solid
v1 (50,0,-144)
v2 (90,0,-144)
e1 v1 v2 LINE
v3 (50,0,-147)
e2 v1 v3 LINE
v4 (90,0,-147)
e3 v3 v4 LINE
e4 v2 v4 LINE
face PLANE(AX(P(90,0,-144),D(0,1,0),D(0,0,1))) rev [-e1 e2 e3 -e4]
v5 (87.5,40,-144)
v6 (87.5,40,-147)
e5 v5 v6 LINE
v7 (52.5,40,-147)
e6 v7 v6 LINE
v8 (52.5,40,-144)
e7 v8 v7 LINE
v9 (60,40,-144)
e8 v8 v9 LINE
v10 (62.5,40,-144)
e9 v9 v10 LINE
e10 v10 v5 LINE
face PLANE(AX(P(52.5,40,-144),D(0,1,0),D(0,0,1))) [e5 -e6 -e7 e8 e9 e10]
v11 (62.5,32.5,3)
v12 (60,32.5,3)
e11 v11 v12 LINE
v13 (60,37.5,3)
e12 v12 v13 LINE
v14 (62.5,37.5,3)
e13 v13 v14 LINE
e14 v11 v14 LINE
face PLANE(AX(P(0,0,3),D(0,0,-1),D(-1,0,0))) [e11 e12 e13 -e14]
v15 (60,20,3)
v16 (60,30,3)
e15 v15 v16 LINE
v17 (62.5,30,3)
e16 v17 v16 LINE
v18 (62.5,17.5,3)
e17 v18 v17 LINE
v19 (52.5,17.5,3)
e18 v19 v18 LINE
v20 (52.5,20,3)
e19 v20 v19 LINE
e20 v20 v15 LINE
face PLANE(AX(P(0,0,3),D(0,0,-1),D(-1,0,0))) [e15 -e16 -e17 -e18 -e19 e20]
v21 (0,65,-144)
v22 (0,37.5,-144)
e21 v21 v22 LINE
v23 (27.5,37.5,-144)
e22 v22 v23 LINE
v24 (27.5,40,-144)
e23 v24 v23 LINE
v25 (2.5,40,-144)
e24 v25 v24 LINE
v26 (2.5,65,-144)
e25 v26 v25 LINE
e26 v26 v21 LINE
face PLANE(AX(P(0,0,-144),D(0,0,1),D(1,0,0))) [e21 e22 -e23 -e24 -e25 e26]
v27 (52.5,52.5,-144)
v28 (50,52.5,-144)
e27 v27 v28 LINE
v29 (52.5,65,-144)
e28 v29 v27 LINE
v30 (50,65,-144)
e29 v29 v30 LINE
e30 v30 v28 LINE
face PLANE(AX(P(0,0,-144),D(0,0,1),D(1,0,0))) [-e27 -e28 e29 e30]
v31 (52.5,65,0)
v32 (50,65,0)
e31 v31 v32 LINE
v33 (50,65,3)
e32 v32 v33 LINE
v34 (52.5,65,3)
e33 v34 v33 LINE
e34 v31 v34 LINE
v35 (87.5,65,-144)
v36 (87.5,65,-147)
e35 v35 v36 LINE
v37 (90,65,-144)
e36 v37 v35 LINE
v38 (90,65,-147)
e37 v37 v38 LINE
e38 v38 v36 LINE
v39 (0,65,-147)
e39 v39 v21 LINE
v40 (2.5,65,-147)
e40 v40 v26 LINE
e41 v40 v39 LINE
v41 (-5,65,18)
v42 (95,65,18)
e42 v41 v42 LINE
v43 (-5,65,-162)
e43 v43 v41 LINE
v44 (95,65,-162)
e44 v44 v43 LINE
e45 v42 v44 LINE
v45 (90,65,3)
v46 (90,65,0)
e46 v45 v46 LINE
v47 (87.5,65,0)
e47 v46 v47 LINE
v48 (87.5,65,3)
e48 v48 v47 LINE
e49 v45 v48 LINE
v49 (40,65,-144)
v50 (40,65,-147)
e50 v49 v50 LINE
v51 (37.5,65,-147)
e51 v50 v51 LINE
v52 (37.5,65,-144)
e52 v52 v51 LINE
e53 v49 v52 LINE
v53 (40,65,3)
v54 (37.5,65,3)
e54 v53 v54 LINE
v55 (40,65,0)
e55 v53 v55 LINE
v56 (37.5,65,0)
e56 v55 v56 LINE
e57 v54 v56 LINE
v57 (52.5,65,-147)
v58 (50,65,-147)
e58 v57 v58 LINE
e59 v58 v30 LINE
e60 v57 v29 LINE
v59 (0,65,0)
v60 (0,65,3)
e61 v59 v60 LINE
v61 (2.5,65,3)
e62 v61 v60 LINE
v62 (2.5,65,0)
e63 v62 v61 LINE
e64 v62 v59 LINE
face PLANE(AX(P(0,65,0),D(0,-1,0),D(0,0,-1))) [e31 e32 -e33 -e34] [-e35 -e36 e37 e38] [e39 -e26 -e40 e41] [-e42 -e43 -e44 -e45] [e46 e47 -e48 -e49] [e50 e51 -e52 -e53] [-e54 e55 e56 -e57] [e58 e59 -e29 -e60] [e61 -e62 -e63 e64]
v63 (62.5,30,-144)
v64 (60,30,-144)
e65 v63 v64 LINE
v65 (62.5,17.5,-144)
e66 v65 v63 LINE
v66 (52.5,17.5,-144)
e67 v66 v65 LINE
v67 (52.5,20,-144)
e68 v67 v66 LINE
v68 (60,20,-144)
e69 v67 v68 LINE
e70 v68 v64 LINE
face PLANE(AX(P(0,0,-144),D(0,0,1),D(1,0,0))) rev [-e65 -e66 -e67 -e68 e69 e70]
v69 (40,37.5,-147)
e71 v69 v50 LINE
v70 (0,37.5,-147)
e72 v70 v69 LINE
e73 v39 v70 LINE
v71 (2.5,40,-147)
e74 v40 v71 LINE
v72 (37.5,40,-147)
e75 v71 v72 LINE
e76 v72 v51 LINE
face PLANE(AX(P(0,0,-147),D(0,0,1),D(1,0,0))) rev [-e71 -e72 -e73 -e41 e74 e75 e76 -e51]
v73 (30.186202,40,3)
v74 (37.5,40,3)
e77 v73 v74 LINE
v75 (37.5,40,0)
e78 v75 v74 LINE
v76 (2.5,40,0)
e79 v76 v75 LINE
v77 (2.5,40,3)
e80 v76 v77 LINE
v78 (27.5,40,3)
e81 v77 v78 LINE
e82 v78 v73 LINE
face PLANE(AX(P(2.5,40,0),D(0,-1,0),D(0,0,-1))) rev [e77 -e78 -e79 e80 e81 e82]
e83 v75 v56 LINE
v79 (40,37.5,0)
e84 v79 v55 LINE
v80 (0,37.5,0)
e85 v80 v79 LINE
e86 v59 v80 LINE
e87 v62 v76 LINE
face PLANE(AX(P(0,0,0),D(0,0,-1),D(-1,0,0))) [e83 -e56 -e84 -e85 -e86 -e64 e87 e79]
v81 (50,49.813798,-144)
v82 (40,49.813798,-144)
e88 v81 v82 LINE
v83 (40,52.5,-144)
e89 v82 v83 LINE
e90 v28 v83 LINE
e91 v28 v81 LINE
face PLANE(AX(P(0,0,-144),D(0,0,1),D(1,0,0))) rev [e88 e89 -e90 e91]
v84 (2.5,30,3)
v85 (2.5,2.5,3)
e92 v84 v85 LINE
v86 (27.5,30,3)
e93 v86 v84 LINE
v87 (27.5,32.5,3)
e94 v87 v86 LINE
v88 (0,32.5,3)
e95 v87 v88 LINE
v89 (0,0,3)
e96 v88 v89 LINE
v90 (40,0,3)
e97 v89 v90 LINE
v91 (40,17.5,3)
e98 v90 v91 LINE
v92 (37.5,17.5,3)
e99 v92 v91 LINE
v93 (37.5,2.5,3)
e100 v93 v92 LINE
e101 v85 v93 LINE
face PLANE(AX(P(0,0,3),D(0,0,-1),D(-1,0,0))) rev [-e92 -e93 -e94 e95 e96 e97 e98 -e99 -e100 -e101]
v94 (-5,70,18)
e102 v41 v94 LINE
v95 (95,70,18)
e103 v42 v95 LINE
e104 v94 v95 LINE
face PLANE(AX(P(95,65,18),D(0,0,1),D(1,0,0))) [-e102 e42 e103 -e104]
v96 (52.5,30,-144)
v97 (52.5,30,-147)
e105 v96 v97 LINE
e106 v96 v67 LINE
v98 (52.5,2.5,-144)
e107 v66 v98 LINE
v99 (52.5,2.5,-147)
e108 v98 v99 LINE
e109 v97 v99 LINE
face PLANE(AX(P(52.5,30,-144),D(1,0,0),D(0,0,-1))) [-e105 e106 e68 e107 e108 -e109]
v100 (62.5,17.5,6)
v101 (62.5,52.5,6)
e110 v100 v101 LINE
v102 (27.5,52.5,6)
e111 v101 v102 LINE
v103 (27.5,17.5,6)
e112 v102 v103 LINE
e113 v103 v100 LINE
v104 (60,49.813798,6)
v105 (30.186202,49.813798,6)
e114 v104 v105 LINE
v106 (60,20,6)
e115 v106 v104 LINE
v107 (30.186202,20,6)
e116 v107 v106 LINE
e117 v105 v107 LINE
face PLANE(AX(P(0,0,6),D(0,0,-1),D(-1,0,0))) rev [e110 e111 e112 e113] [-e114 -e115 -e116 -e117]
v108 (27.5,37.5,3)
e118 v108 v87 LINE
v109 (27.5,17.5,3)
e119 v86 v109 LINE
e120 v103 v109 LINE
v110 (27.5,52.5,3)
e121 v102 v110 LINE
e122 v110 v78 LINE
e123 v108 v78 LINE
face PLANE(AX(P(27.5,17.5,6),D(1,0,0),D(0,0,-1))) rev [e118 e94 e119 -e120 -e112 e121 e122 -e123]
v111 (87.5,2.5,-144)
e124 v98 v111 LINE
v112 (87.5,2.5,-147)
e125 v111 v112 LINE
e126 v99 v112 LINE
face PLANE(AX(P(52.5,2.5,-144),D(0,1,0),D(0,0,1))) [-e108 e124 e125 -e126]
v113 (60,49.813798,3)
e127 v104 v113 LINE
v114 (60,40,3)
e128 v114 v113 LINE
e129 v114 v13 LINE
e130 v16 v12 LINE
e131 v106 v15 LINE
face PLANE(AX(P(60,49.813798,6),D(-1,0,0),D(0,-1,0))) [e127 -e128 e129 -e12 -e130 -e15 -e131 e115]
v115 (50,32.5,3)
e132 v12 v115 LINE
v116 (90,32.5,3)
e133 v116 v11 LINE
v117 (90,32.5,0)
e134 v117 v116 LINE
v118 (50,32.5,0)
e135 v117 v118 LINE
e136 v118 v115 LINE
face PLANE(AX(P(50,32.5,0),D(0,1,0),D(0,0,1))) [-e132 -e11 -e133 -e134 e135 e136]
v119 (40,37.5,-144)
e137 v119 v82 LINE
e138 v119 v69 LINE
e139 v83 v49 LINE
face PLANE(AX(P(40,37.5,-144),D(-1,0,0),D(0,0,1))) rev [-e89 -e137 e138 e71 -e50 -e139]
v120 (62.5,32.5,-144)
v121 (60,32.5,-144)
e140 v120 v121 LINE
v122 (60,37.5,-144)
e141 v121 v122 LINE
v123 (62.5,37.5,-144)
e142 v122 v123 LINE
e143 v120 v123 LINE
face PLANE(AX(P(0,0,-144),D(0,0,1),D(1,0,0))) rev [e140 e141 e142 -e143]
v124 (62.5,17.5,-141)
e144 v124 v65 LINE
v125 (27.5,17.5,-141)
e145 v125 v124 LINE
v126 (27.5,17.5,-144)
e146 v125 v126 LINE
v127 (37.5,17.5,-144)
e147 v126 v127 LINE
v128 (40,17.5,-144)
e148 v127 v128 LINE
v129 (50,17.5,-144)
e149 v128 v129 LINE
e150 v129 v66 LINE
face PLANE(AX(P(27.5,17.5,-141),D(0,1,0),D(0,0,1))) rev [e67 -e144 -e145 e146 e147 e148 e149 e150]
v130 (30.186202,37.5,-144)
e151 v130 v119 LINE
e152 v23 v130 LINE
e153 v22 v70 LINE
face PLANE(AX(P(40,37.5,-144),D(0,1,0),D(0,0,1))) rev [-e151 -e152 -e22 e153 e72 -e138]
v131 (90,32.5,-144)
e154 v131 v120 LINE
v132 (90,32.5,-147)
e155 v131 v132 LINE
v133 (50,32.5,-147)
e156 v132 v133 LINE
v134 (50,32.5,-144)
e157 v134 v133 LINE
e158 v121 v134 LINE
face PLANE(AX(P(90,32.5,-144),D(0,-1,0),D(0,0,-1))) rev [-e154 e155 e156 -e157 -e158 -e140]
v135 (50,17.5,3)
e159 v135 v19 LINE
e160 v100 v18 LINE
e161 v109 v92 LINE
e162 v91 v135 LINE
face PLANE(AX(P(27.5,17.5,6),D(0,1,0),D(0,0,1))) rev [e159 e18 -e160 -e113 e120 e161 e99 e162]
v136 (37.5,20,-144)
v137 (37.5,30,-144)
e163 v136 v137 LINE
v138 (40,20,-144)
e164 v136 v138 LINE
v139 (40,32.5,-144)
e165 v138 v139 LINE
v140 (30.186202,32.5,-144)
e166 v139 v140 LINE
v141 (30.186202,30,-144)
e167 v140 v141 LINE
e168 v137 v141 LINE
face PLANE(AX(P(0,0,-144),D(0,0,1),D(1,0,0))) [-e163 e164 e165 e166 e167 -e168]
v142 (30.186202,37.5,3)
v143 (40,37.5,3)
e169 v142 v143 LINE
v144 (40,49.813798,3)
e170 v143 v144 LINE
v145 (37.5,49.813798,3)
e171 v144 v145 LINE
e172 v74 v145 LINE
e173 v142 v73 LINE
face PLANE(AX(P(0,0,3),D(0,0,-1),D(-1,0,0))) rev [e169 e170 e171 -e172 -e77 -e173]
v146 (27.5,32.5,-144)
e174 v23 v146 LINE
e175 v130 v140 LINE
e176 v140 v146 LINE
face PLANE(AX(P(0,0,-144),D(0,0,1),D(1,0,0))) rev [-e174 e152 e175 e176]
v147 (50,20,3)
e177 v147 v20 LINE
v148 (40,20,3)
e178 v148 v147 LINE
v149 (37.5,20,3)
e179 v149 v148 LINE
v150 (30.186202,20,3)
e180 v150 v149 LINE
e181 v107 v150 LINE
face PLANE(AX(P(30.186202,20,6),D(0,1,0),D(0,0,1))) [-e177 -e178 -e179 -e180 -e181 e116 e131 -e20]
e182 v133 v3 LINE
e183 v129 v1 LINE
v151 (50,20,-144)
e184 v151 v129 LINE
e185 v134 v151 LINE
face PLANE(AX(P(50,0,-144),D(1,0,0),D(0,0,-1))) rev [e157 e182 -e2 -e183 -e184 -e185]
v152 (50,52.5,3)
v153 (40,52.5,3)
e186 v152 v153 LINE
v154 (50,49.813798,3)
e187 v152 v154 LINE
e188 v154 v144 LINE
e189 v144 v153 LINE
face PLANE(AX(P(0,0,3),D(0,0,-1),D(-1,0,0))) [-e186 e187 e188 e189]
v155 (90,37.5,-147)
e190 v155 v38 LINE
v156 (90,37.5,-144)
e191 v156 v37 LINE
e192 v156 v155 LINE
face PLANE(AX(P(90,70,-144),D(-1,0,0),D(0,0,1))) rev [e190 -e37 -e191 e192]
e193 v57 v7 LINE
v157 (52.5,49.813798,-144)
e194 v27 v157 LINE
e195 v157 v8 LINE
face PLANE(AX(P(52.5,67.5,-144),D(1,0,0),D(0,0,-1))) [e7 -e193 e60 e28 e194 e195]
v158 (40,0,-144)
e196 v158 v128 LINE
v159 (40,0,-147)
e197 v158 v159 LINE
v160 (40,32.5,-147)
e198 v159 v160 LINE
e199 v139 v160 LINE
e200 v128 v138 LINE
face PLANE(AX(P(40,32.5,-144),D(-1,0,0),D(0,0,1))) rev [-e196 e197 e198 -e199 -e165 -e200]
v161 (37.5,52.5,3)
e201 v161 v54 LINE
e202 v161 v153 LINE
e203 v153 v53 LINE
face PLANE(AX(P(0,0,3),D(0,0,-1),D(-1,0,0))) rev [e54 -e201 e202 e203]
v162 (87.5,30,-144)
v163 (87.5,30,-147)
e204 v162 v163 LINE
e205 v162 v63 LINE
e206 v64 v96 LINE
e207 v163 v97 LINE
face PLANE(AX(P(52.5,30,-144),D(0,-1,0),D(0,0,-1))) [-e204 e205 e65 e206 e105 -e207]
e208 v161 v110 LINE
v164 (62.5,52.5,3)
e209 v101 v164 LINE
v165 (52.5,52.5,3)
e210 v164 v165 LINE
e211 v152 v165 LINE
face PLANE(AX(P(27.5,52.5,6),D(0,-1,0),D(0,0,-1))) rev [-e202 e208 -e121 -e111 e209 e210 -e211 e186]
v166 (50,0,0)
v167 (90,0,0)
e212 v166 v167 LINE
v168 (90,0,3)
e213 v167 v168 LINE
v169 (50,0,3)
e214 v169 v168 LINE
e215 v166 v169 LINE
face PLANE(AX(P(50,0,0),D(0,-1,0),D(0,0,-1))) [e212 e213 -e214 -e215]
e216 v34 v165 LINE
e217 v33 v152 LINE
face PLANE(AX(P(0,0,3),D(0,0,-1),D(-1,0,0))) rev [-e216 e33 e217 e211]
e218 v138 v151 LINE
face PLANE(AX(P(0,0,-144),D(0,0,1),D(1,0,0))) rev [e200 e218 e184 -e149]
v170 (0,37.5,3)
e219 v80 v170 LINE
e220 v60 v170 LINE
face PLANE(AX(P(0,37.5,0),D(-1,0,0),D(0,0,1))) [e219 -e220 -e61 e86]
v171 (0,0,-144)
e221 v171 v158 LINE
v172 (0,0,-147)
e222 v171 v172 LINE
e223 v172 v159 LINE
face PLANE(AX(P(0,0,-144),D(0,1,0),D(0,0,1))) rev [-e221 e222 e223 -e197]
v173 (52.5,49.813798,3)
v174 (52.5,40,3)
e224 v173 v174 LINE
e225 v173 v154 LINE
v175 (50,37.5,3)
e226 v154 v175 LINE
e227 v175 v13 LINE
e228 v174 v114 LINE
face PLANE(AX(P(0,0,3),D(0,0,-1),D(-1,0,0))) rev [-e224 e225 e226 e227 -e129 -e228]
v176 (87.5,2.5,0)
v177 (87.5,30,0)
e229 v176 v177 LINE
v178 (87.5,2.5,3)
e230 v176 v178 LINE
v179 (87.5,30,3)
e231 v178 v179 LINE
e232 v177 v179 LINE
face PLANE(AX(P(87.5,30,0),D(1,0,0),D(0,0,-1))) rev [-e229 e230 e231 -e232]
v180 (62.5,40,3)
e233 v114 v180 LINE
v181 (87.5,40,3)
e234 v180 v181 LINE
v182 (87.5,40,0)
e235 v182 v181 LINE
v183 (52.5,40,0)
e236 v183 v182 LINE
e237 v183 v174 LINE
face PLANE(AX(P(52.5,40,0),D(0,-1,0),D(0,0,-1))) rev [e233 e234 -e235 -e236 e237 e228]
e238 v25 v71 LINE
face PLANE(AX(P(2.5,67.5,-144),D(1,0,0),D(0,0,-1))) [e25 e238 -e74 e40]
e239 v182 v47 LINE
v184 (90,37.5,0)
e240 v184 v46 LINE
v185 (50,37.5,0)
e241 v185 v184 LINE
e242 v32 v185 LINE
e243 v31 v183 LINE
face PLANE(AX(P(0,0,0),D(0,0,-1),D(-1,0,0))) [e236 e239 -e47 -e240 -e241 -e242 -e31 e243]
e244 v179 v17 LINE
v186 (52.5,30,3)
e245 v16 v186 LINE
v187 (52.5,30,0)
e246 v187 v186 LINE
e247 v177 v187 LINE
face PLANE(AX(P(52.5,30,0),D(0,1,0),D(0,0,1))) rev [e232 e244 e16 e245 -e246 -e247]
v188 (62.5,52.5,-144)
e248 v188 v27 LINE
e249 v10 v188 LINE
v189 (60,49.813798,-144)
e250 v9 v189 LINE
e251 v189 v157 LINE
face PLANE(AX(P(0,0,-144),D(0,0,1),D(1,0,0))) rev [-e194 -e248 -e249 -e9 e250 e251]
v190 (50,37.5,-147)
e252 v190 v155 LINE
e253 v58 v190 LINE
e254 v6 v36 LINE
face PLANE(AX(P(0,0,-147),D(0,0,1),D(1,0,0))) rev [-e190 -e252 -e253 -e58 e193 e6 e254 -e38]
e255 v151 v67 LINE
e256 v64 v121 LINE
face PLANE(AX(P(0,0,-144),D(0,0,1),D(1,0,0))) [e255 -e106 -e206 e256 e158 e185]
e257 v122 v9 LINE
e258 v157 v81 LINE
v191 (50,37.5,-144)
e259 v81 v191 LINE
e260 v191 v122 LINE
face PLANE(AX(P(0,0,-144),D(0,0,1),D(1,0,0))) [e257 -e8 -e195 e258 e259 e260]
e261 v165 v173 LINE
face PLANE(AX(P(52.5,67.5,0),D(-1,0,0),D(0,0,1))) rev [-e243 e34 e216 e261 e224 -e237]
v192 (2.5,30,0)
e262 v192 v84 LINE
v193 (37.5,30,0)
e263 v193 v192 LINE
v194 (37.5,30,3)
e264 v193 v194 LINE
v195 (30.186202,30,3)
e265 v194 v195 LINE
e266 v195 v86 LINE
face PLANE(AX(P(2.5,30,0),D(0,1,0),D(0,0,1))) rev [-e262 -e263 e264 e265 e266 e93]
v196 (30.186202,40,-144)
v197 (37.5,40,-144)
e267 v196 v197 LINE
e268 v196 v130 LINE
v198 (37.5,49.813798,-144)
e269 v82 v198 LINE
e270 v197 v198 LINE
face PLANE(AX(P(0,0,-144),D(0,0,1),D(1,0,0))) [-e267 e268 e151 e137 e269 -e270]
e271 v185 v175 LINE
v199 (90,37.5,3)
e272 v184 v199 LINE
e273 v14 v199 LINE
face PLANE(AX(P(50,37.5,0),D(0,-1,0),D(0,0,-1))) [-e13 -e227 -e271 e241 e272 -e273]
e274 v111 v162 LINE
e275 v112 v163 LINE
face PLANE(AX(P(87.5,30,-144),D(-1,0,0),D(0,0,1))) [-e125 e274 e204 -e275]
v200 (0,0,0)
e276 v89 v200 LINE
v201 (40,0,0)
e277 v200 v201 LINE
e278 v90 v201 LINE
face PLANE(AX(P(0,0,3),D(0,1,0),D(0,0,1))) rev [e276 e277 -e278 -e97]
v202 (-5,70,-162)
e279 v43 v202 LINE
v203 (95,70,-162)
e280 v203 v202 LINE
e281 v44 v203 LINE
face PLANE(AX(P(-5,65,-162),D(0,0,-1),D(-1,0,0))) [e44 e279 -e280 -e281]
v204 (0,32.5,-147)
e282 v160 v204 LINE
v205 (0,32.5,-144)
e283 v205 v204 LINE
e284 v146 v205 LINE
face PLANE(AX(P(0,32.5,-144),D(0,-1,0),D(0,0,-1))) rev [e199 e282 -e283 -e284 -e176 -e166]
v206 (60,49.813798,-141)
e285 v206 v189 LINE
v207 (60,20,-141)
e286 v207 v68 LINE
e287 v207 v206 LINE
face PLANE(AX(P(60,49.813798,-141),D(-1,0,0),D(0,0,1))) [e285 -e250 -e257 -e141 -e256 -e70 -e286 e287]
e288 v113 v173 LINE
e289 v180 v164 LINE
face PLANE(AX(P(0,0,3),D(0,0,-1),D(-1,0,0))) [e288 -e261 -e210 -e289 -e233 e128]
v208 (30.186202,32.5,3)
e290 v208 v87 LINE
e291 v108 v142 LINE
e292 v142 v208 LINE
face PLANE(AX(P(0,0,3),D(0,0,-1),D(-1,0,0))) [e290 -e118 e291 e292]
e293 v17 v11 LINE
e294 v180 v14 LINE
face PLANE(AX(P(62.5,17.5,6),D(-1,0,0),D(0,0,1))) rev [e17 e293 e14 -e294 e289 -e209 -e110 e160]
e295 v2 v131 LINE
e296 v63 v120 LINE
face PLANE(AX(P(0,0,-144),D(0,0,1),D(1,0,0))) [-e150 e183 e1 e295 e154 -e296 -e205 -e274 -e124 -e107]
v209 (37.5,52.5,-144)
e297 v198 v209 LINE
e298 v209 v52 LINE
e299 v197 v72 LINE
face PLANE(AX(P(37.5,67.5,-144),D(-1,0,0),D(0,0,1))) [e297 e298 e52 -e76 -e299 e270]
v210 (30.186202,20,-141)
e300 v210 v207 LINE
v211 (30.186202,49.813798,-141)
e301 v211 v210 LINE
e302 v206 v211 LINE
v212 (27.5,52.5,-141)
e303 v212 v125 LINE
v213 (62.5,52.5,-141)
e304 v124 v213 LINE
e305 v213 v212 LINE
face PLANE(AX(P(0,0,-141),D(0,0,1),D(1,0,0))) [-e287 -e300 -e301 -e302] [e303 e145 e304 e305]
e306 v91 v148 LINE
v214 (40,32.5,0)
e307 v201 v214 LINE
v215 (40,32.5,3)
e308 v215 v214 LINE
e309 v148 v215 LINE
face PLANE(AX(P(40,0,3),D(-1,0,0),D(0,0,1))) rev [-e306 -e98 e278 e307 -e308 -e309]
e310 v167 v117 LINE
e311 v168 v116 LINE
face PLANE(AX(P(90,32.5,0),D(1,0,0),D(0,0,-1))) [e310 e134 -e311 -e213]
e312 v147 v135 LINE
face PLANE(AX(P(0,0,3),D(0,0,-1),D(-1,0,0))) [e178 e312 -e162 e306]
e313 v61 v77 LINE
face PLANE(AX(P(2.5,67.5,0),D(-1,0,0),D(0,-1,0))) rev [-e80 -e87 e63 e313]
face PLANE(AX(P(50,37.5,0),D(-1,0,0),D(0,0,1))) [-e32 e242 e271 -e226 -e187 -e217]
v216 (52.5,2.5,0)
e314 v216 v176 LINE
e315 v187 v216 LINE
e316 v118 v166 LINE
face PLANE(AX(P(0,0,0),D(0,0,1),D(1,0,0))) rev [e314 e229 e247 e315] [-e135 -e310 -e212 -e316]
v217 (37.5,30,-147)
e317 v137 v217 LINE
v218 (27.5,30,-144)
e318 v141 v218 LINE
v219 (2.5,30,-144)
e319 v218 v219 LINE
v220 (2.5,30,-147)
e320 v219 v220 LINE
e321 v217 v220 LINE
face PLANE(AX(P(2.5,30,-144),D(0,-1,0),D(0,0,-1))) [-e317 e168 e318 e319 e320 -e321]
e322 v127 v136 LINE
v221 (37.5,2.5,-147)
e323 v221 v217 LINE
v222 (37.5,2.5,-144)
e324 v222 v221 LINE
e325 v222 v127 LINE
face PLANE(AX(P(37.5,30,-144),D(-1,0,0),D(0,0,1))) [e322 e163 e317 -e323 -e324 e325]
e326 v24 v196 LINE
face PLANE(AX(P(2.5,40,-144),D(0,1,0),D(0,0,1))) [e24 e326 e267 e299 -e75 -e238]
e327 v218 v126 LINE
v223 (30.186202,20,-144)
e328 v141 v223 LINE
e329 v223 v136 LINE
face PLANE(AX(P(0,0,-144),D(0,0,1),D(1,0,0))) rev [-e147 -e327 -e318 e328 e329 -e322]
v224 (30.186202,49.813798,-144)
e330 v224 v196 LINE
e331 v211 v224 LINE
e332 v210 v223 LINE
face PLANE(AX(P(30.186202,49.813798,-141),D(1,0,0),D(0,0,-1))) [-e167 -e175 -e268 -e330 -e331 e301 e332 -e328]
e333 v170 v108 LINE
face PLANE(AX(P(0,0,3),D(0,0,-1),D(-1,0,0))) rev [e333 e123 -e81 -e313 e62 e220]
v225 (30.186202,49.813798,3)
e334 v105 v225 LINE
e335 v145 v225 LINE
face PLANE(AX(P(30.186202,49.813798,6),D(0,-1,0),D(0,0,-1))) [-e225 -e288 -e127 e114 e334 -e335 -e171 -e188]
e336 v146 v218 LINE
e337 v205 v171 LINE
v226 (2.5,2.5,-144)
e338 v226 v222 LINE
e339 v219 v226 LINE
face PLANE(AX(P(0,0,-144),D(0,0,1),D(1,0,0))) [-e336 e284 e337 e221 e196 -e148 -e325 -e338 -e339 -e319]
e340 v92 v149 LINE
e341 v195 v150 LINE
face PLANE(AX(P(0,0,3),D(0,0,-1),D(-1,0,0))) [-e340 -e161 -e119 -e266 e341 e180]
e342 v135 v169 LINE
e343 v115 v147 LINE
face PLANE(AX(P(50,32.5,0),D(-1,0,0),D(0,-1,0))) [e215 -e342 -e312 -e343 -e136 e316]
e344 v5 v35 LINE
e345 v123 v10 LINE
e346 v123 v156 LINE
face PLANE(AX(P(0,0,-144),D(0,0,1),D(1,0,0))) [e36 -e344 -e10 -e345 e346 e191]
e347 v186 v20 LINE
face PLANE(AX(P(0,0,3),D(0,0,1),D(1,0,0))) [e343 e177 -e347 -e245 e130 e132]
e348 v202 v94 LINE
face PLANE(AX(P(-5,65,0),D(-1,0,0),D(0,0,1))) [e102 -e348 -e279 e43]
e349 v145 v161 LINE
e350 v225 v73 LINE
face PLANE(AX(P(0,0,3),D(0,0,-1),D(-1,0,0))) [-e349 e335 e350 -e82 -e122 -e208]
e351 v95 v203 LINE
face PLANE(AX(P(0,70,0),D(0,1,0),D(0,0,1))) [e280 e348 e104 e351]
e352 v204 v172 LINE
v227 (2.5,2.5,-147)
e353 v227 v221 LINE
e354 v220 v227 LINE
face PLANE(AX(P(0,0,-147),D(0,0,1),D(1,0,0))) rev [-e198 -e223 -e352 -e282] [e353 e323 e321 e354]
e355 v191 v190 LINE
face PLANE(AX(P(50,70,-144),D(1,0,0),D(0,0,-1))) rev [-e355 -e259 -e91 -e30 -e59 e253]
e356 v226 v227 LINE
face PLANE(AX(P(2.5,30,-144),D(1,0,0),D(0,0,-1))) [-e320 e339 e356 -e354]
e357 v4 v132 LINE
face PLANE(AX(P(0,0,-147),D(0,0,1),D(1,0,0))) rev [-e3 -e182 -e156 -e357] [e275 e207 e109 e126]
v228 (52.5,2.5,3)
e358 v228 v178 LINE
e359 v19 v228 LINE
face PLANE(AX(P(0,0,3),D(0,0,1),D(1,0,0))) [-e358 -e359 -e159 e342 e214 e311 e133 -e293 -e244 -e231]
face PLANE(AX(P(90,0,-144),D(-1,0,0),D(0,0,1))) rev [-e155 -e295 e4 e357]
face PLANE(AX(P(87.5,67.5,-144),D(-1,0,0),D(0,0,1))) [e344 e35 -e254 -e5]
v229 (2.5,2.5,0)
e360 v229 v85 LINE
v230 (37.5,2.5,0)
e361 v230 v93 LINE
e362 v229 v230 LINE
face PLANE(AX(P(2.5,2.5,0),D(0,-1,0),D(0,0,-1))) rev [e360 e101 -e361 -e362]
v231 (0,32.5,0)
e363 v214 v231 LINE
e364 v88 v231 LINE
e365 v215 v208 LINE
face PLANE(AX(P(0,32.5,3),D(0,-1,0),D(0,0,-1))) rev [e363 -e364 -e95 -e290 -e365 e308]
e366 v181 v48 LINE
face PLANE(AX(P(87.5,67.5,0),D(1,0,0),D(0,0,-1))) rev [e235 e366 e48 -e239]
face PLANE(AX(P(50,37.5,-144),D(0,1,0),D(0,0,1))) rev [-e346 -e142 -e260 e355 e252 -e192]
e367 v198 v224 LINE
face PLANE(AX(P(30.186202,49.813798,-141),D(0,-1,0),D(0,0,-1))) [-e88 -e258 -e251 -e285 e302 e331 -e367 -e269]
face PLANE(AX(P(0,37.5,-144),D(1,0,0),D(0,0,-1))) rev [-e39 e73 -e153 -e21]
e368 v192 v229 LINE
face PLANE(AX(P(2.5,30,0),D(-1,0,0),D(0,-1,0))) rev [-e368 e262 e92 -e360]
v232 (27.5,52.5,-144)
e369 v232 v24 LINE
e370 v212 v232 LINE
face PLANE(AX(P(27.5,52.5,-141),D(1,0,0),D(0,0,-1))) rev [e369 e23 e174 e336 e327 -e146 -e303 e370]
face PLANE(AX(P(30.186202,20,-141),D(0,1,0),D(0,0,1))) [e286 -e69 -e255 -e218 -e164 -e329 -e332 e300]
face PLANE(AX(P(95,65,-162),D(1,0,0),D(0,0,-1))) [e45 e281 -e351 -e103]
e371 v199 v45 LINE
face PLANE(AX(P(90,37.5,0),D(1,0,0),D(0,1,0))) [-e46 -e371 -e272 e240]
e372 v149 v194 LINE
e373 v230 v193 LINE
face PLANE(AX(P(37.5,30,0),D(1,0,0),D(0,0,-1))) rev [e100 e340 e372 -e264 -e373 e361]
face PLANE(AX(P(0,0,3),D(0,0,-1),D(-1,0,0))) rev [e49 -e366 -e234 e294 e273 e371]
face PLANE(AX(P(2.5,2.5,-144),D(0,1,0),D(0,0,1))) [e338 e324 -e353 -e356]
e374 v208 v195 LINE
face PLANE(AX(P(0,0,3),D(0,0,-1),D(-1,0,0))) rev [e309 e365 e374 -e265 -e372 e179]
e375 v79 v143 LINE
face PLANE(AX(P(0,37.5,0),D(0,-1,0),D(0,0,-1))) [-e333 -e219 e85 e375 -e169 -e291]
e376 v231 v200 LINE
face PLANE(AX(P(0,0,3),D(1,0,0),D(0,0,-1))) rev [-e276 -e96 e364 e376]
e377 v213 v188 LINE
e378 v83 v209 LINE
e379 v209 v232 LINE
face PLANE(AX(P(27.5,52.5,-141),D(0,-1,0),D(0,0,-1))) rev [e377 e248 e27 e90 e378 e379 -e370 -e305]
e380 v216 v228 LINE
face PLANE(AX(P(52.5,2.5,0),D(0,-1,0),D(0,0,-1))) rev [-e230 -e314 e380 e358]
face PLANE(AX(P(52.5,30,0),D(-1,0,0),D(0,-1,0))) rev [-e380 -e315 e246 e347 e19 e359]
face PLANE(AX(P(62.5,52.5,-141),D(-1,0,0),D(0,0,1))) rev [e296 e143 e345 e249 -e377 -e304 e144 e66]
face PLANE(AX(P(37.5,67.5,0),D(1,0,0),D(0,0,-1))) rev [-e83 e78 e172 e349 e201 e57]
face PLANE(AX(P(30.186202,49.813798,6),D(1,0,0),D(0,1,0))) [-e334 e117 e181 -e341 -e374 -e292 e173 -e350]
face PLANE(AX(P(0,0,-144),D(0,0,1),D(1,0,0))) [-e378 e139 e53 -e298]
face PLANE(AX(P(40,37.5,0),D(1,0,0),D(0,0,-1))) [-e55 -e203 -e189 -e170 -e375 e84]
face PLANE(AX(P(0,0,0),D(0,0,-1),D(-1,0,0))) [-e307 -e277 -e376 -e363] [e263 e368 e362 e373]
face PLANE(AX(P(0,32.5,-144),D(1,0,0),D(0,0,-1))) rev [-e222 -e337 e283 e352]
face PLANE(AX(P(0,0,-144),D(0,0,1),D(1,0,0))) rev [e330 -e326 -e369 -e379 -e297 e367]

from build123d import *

# Parameters (mm, degrees)
FRONT_FRAME_PANEL_SKETCH_W      = 40
FRONT_FRAME_PANEL_SKETCH_H      = 32.5
FRONT_FRAME_PANEL_40X32_5_DEPTH = 3
FRONT_FRAME_SIDE_SKETCH_W       = 40
FRONT_FRAME_SIDE_SKETCH_H       = 32.5
FRONT_FRAME_SIDE_DEPTH          = 3
FRONT_FRAME_OUTER_SKETCH_W      = 40
FRONT_FRAME_OUTER_SKETCH_H      = 32.5
FRONT_FRAME_OUTER_DEPTH         = 3
FRONT_FRAME_OUTER_2_DEPTH       = 3
FRAME_WINDOW_CUT_SKETCH_W       = 35
FRAME_WINDOW_CUT_SKETCH_H       = 27.5
FRAME_WINDOW_CUT_DEPTH          = 3
FRONT_SQUARE_FRAME_SKETCH_W     = 35
FRONT_SQUARE_FRAME_SKETCH_H     = 35
FRONT_SQUARE_FRAME_SKETCH_W_2   = 29.813797942
FRONT_SQUARE_FRAME_SKETCH_H_2   = 29.813797942
FRONT_SQUARE_FRAME_35X35_DEPTH  = 3
REAR_FRAME_A_SKETCH_W           = 40
REAR_FRAME_A_SKETCH_H           = 32.5
REAR_FRAME_A_SKETCH_W_2         = 35
REAR_FRAME_A_SKETCH_H_2         = 27.5
REAR_FRAME_A_DEPTH              = 3
REAR_FRAME_B_SKETCH_W           = 40
REAR_FRAME_B_SKETCH_H           = 32.5
REAR_FRAME_B_SKETCH_W_2         = 35
REAR_FRAME_B_SKETCH_H_2         = 27.5
REAR_FRAME_B_DEPTH              = 3
REAR_FRAME_C_SKETCH_W           = 40
REAR_FRAME_C_SKETCH_H           = 32.5
REAR_FRAME_C_SKETCH_W_2         = 35
REAR_FRAME_C_SKETCH_H_2         = 27.5
REAR_FRAME_C_DEPTH              = 3
REAR_FRAME_D_SKETCH_W           = 40
REAR_FRAME_D_SKETCH_H           = 32.5
REAR_FRAME_D_SKETCH_W_2         = 35
REAR_FRAME_D_SKETCH_H_2         = 27.5
REAR_FRAME_D_DEPTH              = 3
REAR_SQUARE_FRAME_SKETCH_W      = 35
REAR_SQUARE_FRAME_SKETCH_H      = 35
REAR_SQUARE_FRAME_SKETCH_W_2    = 29.813797942
REAR_SQUARE_FRAME_SKETCH_H_2    = 29.813797942
REAR_SQUARE_FRAME_DEPTH         = 3
TABLE_TOP_162X100X5_DEPTH       = 5


with BuildPart() as part:
    # Front Frame Panel Sketch → Front Frame Panel 40x32.5 (new body)
    with BuildSketch(Plane.XY):
        with Locations((20, 16.25)):
            Rectangle(FRONT_FRAME_PANEL_SKETCH_W, FRONT_FRAME_PANEL_SKETCH_H)
    extrude(amount=FRONT_FRAME_PANEL_40X32_5_DEPTH)


with BuildPart() as body_2:
    # Front Frame Side Sketch → Front Frame Side (new body)
    with BuildSketch(Plane.XY.offset(3)):
        with Locations((70, 16.25)):
            Rectangle(FRONT_FRAME_SIDE_SKETCH_W, FRONT_FRAME_SIDE_SKETCH_H)
    extrude(amount=-FRONT_FRAME_SIDE_DEPTH)


with BuildPart() as body_3:
    # Front Frame Outer Sketch → Front Frame Outer (new body)
    with BuildSketch(Plane.XY.offset(3)):
        with Locations((20, 53.75)):
            Rectangle(FRONT_FRAME_OUTER_SKETCH_W, FRONT_FRAME_OUTER_SKETCH_H)
    extrude(amount=-FRONT_FRAME_OUTER_DEPTH)


with BuildPart() as body_4:
    # Front Frame Outer Sketch → Front Frame Outer 2 (new body)
    with BuildSketch(Plane.XY.offset(3)):
        with Locations((70, 53.75)):
            Rectangle(FRONT_FRAME_OUTER_SKETCH_W, FRONT_FRAME_OUTER_SKETCH_H)
    extrude(amount=-FRONT_FRAME_OUTER_2_DEPTH)


with BuildPart() as frame_window_cut_tool:
    # Frame Window Cut Sketch → Frame Window Cut (new body)
    with BuildSketch(Plane.XY.offset(3)):
        with Locations((20, 16.25)):
            Rectangle(FRAME_WINDOW_CUT_SKETCH_W, FRAME_WINDOW_CUT_SKETCH_H)
        with Locations((70, 16.25)):
            Rectangle(FRAME_WINDOW_CUT_SKETCH_W, FRAME_WINDOW_CUT_SKETCH_H)
        with Locations((20, 53.75)):
            Rectangle(FRAME_WINDOW_CUT_SKETCH_W, FRAME_WINDOW_CUT_SKETCH_H)
        with Locations((70, 53.75)):
            Rectangle(FRAME_WINDOW_CUT_SKETCH_W, FRAME_WINDOW_CUT_SKETCH_H)
    extrude(amount=-FRAME_WINDOW_CUT_DEPTH)


with BuildPart() as part_1:
    add(part.part)

    # Frame Window Cut: cut by frame_window_cut_tool
    add(frame_window_cut_tool.part, mode=Mode.SUBTRACT)



with BuildPart() as body_2_1:
    add(body_2.part)

    # Frame Window Cut: cut by frame_window_cut_tool
    add(frame_window_cut_tool.part, mode=Mode.SUBTRACT)


with BuildPart() as body_3_1:
    add(body_3.part)

    # Frame Window Cut: cut by frame_window_cut_tool
    add(frame_window_cut_tool.part, mode=Mode.SUBTRACT)


with BuildPart() as body_4_1:
    add(body_4.part)

    # Frame Window Cut: cut by frame_window_cut_tool
    add(frame_window_cut_tool.part, mode=Mode.SUBTRACT)


with BuildPart() as part_2:
    add(part_1.part)

    add(body_2_1.part)  # Front Square Frame 35x35 merges body 2

    add(body_3_1.part)  # Front Square Frame 35x35 merges body 3

    add(body_4_1.part)  # Front Square Frame 35x35 merges body 4
    # Front Square Frame Sketch → Front Square Frame 35x35 (add)
    with BuildSketch(Plane.XY.offset(3)):
        with Locations((45, 35)):
            Rectangle(FRONT_SQUARE_FRAME_SKETCH_W, FRONT_SQUARE_FRAME_SKETCH_H)
        with Locations((45.093101029, 34.906898971)):
            Rectangle(FRONT_SQUARE_FRAME_SKETCH_W_2, FRONT_SQUARE_FRAME_SKETCH_H_2, mode=Mode.SUBTRACT)
    extrude(amount=FRONT_SQUARE_FRAME_35X35_DEPTH)



with BuildPart() as body_2_2:
    # Rear Frame A Sketch → Rear Frame A (new body)
    with BuildSketch(Plane.XY.offset(-147)):
        with Locations((70, 16.25)):
            Rectangle(REAR_FRAME_A_SKETCH_W, REAR_FRAME_A_SKETCH_H)
        with Locations((70, 16.25)):
            Rectangle(REAR_FRAME_A_SKETCH_W_2, REAR_FRAME_A_SKETCH_H_2, mode=Mode.SUBTRACT)
    extrude(amount=REAR_FRAME_A_DEPTH)



with BuildPart() as body_3_2:
    # Rear Frame B Sketch → Rear Frame B (new body)
    with BuildSketch(Plane.XY.offset(-147)):
        with Locations((20, 16.25)):
            Rectangle(REAR_FRAME_B_SKETCH_W, REAR_FRAME_B_SKETCH_H)
        with Locations((20, 16.25)):
            Rectangle(REAR_FRAME_B_SKETCH_W_2, REAR_FRAME_B_SKETCH_H_2, mode=Mode.SUBTRACT)
    extrude(amount=REAR_FRAME_B_DEPTH)


with BuildPart() as body_4_2:
    # Rear Frame C Sketch → Rear Frame C (new body)
    with BuildSketch(Plane.XY.offset(-147)):
        with Locations((20, 53.75)):
            Rectangle(REAR_FRAME_C_SKETCH_W, REAR_FRAME_C_SKETCH_H)
        with Locations((20, 53.75)):
            Rectangle(REAR_FRAME_C_SKETCH_W_2, REAR_FRAME_C_SKETCH_H_2, mode=Mode.SUBTRACT)
    extrude(amount=REAR_FRAME_C_DEPTH)


with BuildPart() as body_5:
    # Rear Frame D Sketch → Rear Frame D (new body)
    with BuildSketch(Plane.XY.offset(-147)):
        with Locations((70, 53.75)):
            Rectangle(REAR_FRAME_D_SKETCH_W, REAR_FRAME_D_SKETCH_H)
        with Locations((70, 53.75)):
            Rectangle(REAR_FRAME_D_SKETCH_W_2, REAR_FRAME_D_SKETCH_H_2, mode=Mode.SUBTRACT)
    extrude(amount=REAR_FRAME_D_DEPTH)


with BuildPart() as body_2_2_1:
    add(body_2_2.part)

    add(body_3_2.part)  # Rear Square Frame merges body 3 2

    add(body_4_2.part)  # Rear Square Frame merges body 4 2

    add(body_5.part)  # Rear Square Frame merges body 5
    # Rear Square Frame Sketch → Rear Square Frame (add)
    with BuildSketch(Plane.XY.offset(-144)):
        with Locations((45, 35)):
            Rectangle(REAR_SQUARE_FRAME_SKETCH_W, REAR_SQUARE_FRAME_SKETCH_H)
        with Locations((45.093101029, 34.906898971)):
            Rectangle(REAR_SQUARE_FRAME_SKETCH_W_2, REAR_SQUARE_FRAME_SKETCH_H_2, mode=Mode.SUBTRACT)
    extrude(amount=REAR_SQUARE_FRAME_DEPTH)


with BuildPart() as part_3:
    add(part_2.part)

    add(body_2_2_1.part)  # Table Top 162x100x5 merges body 2 2
    # Table Top Sketch → Table Top 162x100x5 (add)
    with BuildSketch(Plane(origin=(0, 70, 0), x_dir=(1, 0, 0), z_dir=(0, 1, 0))):
        Polygon((-5, 0), (-5, 162), (95, 162), (95, -18), (-5, -18), align=None)
    extrude(amount=-TABLE_TOP_162X100X5_DEPTH)


solid = part_3.part
